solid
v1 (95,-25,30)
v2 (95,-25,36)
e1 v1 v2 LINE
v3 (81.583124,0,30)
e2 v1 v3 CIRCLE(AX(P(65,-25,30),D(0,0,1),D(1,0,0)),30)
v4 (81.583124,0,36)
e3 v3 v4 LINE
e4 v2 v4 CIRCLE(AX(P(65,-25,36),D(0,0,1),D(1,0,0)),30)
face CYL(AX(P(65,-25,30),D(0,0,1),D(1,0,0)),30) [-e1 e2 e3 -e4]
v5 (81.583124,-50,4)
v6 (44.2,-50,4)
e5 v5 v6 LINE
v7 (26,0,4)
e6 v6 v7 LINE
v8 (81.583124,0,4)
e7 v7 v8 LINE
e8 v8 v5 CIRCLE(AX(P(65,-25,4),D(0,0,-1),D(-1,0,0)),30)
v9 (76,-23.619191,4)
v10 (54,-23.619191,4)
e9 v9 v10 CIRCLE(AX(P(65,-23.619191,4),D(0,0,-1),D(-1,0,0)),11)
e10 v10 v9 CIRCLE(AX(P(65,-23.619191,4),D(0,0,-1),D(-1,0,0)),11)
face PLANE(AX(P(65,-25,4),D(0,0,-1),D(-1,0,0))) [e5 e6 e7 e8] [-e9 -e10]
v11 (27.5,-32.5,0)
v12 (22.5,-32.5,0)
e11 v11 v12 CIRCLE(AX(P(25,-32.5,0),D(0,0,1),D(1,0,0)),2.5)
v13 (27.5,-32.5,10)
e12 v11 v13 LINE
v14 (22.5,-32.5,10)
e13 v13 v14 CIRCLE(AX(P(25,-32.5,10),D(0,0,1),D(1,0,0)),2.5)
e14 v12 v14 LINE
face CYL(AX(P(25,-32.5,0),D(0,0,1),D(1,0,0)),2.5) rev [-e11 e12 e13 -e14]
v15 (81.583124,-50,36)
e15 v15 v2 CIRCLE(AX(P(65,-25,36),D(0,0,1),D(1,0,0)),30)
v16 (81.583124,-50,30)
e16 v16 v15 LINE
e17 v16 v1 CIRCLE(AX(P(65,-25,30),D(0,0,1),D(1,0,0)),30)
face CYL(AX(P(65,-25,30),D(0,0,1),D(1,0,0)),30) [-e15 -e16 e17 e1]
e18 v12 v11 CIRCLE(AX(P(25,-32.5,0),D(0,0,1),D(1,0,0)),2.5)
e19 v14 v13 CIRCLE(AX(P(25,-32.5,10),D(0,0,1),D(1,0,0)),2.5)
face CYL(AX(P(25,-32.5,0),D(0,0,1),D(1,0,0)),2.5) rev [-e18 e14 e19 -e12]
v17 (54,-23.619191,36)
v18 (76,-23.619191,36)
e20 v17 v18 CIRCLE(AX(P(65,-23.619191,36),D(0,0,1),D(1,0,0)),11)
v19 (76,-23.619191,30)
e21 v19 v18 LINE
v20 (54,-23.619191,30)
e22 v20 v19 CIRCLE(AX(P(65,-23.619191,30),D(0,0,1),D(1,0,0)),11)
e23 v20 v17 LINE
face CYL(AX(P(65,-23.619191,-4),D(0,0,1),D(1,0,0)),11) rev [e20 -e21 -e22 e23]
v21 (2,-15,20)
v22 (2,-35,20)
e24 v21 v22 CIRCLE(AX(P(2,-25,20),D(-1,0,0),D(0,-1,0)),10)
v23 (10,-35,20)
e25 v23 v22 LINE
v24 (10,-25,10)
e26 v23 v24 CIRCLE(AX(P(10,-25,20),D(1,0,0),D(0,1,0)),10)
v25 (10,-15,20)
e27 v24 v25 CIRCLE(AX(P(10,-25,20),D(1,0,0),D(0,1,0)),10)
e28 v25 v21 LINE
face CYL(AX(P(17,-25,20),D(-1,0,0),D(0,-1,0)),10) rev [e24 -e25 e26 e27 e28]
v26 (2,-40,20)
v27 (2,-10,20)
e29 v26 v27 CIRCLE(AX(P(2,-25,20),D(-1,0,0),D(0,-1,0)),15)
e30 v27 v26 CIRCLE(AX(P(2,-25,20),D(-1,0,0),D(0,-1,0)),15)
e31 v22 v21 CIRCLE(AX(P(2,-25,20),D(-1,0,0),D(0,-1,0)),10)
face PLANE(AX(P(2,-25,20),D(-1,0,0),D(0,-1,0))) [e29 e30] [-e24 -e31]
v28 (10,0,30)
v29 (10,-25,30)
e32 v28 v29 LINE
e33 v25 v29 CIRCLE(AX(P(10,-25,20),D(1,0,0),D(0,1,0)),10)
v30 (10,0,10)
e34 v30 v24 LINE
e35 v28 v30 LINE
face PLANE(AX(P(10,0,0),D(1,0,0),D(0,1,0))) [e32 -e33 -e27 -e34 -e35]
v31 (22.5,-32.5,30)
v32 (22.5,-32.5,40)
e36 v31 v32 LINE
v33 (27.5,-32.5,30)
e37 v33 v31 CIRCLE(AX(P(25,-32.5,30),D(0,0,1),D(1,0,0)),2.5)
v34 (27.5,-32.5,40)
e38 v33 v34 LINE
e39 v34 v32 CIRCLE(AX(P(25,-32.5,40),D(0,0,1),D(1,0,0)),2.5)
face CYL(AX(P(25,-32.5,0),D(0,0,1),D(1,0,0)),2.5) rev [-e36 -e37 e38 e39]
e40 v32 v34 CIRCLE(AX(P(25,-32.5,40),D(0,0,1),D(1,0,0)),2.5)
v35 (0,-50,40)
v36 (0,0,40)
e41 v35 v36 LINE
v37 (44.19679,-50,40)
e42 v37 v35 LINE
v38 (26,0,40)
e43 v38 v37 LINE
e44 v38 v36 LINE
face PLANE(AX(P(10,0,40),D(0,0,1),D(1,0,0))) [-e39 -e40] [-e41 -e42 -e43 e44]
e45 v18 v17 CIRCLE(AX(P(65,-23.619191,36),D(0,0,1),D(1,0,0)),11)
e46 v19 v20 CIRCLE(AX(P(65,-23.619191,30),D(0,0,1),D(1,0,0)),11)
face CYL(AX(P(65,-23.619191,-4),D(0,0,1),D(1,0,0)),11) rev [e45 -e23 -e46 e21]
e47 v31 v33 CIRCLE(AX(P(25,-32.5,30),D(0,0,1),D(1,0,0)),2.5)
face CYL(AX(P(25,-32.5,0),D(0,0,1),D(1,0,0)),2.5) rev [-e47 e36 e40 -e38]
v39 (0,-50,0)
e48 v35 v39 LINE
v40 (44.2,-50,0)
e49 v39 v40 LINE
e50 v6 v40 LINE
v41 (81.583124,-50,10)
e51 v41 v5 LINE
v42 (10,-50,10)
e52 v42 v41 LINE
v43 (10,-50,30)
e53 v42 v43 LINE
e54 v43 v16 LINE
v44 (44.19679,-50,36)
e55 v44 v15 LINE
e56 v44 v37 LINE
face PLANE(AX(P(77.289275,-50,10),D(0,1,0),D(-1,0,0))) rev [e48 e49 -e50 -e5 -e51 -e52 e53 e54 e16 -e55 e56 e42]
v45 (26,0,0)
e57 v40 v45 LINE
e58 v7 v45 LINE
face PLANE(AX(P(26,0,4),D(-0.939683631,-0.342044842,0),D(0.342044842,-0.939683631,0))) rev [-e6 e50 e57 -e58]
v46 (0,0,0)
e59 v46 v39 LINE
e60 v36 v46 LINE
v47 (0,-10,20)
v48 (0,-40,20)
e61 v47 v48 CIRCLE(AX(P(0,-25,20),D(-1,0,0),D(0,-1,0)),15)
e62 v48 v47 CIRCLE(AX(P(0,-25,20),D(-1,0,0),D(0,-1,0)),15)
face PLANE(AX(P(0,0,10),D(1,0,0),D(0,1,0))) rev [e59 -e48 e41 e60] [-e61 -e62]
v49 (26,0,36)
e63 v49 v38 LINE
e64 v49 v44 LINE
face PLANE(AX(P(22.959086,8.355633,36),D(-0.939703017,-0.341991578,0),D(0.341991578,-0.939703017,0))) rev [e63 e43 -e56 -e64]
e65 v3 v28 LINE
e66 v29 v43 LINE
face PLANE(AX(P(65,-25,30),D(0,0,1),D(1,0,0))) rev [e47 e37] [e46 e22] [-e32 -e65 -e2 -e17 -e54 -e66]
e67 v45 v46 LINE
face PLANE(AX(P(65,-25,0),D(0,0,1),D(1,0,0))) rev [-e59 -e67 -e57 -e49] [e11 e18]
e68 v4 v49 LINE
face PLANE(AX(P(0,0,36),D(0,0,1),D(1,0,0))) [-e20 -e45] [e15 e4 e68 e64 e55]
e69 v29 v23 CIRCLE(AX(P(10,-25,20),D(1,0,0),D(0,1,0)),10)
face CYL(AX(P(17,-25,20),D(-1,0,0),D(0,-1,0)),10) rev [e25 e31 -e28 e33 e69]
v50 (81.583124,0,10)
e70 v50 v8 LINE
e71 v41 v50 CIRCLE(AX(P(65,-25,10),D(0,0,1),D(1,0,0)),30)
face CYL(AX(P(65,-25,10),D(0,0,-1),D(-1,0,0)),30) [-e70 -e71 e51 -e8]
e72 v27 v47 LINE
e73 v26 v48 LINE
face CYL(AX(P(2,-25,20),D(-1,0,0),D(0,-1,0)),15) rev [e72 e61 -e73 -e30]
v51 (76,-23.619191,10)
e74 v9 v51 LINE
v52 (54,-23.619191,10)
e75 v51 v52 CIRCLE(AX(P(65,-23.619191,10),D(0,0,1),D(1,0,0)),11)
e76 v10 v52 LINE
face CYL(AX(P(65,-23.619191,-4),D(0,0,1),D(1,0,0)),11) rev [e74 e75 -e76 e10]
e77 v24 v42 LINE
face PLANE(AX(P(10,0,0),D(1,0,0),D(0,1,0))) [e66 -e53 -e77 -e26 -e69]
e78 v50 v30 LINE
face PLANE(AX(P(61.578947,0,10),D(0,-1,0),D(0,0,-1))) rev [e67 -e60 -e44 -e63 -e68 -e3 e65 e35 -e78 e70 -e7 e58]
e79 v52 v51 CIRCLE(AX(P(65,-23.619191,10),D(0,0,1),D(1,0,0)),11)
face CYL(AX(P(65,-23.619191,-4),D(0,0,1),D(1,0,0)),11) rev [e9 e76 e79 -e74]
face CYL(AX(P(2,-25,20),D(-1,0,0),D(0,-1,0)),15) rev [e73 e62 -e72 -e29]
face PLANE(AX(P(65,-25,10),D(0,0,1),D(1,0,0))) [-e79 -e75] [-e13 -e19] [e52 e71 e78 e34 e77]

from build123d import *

# Parameters (mm, degrees)
SIDE_PLATE_DEPTH           = 10
MOUNTING_BLOCK_SKETCH_W    = 30
MOUNTING_BLOCK_SKETCH_H    = 50
MOUNTING_BLOCK_DEPTH       = 10
SECOND_START               = -10
SECOND_SIDE_PLATE_DEPTH    = 10
TOP_START                  = -4
TOP_RECESS_4MM_DEPTH       = 4
SIDE_RECESS_4MM_DEPTH      = 4
CROSS_HOLE_SKETCH_R        = 11
CROSS_HOLE_DEPTH           = 40
SPOT_FACE_SKETCH_R         = 15
SPOT_FACE_2MM_DEPTH        = 2
SMALL_HOLE_SKETCH_R        = 10
SMALL_HOLE_15MM_DEEP_DEPTH = 15
PIN_HOLE_SKETCH_R          = 2.5
PIN_HOLE_DEPTH             = 40


with BuildPart() as part:
    # Side Plate Sketch → Side Plate (new body)
    with BuildSketch(Plane.XY):
        with BuildLine():
            Line((0, 0), (0, -50))
            Line((0, -50), (61.578947368, -50))
            Line((61.578947368, -50), (77.289275323, -50))
            Line((77.289275323, -50), (81.583123952, -50))
            ThreePointArc((81.583123952, -50), (95, -25), (81.583123952, 0))
            Line((81.583123952, 0), (77.289275323, 0))
            Line((77.289275323, 0), (61.578947368, 0))
            Line((61.578947368, 0), (0, 0))
        make_face()
    extrude(amount=SIDE_PLATE_DEPTH)

    # Mounting Block Sketch → Mounting Block (add)
    with BuildSketch(Plane.ZY):
        with Locations((25, -25)):
            Rectangle(MOUNTING_BLOCK_SKETCH_W, MOUNTING_BLOCK_SKETCH_H)
    extrude(amount=-MOUNTING_BLOCK_DEPTH)

    # Second Plate Sketch → Second Side Plate (add)
    with BuildSketch(Plane.XY.offset(40).offset(SECOND_START)):
        with BuildLine():
            Line((10, 0), (81.583123952, 0))
            ThreePointArc((81.583123952, 0), (95, -25), (81.583123952, -50))
            Line((81.583123952, -50), (10, -50))
            Line((10, -50), (10, 0))
        make_face()
    extrude(amount=SECOND_SIDE_PLATE_DEPTH)

    # Top Recess Sketch → Top Recess 4mm (cut)
    with BuildSketch(Plane.XY.offset(40).offset(TOP_START)):
        with BuildLine():
            Line((81.583123952, 0), (26, 0))
            Line((26, 0), (44.196790465, -50))
            Line((44.196790465, -50), (81.583123952, -50))
            ThreePointArc((81.583123952, -50), (95, -25), (81.583123952, 0))
        make_face()
    extrude(amount=TOP_RECESS_4MM_DEPTH, mode=Mode.SUBTRACT)

    # Side Recess Sketch → Side Recess 4mm (cut)
    with BuildSketch(Plane(origin=(0, 0, 0), x_dir=(-1, 0, 0), z_dir=(0, 0, -1))):
        with BuildLine():
            Line((-26, 0), (-44.2, -50))
            Line((-44.2, -50), (-81.583123952, -50))
            ThreePointArc((-81.583123952, -50), (-95, -25), (-81.583123952, 0))
            Line((-81.583123952, 0), (-26, 0))
        make_face()
    extrude(amount=-SIDE_RECESS_4MM_DEPTH, mode=Mode.SUBTRACT)

    # Cross Hole Sketch → Cross Hole (cut)
    with BuildSketch(Plane.XY.offset(36)):
        with Locations((65, -23.619190871)):
            Circle(CROSS_HOLE_SKETCH_R)
    extrude(amount=-CROSS_HOLE_DEPTH, mode=Mode.SUBTRACT)

    # Spot Face Sketch → Spot Face 2mm (cut)
    with BuildSketch(Plane.ZY):
        with Locations(Location((20, -25, 0), (0, 0, 270))):
            Circle(SPOT_FACE_SKETCH_R)
    extrude(amount=-SPOT_FACE_2MM_DEPTH, mode=Mode.SUBTRACT)

    # Small Hole Sketch → Small Hole 15mm Deep (cut)
    with BuildSketch(Plane.ZY.offset(-2)):
        with Locations(Location((20, -25, 0), (0, 0, 270))):
            Circle(SMALL_HOLE_SKETCH_R)
    extrude(amount=-SMALL_HOLE_15MM_DEEP_DEPTH, mode=Mode.SUBTRACT)

    # Pin Hole Sketch → Pin Hole (cut)
    with BuildSketch(Plane.XY.offset(40)):
        with Locations((25, -32.5)):
            Circle(PIN_HOLE_SKETCH_R)
    extrude(amount=-PIN_HOLE_DEPTH, mode=Mode.SUBTRACT)


solid = part.part
